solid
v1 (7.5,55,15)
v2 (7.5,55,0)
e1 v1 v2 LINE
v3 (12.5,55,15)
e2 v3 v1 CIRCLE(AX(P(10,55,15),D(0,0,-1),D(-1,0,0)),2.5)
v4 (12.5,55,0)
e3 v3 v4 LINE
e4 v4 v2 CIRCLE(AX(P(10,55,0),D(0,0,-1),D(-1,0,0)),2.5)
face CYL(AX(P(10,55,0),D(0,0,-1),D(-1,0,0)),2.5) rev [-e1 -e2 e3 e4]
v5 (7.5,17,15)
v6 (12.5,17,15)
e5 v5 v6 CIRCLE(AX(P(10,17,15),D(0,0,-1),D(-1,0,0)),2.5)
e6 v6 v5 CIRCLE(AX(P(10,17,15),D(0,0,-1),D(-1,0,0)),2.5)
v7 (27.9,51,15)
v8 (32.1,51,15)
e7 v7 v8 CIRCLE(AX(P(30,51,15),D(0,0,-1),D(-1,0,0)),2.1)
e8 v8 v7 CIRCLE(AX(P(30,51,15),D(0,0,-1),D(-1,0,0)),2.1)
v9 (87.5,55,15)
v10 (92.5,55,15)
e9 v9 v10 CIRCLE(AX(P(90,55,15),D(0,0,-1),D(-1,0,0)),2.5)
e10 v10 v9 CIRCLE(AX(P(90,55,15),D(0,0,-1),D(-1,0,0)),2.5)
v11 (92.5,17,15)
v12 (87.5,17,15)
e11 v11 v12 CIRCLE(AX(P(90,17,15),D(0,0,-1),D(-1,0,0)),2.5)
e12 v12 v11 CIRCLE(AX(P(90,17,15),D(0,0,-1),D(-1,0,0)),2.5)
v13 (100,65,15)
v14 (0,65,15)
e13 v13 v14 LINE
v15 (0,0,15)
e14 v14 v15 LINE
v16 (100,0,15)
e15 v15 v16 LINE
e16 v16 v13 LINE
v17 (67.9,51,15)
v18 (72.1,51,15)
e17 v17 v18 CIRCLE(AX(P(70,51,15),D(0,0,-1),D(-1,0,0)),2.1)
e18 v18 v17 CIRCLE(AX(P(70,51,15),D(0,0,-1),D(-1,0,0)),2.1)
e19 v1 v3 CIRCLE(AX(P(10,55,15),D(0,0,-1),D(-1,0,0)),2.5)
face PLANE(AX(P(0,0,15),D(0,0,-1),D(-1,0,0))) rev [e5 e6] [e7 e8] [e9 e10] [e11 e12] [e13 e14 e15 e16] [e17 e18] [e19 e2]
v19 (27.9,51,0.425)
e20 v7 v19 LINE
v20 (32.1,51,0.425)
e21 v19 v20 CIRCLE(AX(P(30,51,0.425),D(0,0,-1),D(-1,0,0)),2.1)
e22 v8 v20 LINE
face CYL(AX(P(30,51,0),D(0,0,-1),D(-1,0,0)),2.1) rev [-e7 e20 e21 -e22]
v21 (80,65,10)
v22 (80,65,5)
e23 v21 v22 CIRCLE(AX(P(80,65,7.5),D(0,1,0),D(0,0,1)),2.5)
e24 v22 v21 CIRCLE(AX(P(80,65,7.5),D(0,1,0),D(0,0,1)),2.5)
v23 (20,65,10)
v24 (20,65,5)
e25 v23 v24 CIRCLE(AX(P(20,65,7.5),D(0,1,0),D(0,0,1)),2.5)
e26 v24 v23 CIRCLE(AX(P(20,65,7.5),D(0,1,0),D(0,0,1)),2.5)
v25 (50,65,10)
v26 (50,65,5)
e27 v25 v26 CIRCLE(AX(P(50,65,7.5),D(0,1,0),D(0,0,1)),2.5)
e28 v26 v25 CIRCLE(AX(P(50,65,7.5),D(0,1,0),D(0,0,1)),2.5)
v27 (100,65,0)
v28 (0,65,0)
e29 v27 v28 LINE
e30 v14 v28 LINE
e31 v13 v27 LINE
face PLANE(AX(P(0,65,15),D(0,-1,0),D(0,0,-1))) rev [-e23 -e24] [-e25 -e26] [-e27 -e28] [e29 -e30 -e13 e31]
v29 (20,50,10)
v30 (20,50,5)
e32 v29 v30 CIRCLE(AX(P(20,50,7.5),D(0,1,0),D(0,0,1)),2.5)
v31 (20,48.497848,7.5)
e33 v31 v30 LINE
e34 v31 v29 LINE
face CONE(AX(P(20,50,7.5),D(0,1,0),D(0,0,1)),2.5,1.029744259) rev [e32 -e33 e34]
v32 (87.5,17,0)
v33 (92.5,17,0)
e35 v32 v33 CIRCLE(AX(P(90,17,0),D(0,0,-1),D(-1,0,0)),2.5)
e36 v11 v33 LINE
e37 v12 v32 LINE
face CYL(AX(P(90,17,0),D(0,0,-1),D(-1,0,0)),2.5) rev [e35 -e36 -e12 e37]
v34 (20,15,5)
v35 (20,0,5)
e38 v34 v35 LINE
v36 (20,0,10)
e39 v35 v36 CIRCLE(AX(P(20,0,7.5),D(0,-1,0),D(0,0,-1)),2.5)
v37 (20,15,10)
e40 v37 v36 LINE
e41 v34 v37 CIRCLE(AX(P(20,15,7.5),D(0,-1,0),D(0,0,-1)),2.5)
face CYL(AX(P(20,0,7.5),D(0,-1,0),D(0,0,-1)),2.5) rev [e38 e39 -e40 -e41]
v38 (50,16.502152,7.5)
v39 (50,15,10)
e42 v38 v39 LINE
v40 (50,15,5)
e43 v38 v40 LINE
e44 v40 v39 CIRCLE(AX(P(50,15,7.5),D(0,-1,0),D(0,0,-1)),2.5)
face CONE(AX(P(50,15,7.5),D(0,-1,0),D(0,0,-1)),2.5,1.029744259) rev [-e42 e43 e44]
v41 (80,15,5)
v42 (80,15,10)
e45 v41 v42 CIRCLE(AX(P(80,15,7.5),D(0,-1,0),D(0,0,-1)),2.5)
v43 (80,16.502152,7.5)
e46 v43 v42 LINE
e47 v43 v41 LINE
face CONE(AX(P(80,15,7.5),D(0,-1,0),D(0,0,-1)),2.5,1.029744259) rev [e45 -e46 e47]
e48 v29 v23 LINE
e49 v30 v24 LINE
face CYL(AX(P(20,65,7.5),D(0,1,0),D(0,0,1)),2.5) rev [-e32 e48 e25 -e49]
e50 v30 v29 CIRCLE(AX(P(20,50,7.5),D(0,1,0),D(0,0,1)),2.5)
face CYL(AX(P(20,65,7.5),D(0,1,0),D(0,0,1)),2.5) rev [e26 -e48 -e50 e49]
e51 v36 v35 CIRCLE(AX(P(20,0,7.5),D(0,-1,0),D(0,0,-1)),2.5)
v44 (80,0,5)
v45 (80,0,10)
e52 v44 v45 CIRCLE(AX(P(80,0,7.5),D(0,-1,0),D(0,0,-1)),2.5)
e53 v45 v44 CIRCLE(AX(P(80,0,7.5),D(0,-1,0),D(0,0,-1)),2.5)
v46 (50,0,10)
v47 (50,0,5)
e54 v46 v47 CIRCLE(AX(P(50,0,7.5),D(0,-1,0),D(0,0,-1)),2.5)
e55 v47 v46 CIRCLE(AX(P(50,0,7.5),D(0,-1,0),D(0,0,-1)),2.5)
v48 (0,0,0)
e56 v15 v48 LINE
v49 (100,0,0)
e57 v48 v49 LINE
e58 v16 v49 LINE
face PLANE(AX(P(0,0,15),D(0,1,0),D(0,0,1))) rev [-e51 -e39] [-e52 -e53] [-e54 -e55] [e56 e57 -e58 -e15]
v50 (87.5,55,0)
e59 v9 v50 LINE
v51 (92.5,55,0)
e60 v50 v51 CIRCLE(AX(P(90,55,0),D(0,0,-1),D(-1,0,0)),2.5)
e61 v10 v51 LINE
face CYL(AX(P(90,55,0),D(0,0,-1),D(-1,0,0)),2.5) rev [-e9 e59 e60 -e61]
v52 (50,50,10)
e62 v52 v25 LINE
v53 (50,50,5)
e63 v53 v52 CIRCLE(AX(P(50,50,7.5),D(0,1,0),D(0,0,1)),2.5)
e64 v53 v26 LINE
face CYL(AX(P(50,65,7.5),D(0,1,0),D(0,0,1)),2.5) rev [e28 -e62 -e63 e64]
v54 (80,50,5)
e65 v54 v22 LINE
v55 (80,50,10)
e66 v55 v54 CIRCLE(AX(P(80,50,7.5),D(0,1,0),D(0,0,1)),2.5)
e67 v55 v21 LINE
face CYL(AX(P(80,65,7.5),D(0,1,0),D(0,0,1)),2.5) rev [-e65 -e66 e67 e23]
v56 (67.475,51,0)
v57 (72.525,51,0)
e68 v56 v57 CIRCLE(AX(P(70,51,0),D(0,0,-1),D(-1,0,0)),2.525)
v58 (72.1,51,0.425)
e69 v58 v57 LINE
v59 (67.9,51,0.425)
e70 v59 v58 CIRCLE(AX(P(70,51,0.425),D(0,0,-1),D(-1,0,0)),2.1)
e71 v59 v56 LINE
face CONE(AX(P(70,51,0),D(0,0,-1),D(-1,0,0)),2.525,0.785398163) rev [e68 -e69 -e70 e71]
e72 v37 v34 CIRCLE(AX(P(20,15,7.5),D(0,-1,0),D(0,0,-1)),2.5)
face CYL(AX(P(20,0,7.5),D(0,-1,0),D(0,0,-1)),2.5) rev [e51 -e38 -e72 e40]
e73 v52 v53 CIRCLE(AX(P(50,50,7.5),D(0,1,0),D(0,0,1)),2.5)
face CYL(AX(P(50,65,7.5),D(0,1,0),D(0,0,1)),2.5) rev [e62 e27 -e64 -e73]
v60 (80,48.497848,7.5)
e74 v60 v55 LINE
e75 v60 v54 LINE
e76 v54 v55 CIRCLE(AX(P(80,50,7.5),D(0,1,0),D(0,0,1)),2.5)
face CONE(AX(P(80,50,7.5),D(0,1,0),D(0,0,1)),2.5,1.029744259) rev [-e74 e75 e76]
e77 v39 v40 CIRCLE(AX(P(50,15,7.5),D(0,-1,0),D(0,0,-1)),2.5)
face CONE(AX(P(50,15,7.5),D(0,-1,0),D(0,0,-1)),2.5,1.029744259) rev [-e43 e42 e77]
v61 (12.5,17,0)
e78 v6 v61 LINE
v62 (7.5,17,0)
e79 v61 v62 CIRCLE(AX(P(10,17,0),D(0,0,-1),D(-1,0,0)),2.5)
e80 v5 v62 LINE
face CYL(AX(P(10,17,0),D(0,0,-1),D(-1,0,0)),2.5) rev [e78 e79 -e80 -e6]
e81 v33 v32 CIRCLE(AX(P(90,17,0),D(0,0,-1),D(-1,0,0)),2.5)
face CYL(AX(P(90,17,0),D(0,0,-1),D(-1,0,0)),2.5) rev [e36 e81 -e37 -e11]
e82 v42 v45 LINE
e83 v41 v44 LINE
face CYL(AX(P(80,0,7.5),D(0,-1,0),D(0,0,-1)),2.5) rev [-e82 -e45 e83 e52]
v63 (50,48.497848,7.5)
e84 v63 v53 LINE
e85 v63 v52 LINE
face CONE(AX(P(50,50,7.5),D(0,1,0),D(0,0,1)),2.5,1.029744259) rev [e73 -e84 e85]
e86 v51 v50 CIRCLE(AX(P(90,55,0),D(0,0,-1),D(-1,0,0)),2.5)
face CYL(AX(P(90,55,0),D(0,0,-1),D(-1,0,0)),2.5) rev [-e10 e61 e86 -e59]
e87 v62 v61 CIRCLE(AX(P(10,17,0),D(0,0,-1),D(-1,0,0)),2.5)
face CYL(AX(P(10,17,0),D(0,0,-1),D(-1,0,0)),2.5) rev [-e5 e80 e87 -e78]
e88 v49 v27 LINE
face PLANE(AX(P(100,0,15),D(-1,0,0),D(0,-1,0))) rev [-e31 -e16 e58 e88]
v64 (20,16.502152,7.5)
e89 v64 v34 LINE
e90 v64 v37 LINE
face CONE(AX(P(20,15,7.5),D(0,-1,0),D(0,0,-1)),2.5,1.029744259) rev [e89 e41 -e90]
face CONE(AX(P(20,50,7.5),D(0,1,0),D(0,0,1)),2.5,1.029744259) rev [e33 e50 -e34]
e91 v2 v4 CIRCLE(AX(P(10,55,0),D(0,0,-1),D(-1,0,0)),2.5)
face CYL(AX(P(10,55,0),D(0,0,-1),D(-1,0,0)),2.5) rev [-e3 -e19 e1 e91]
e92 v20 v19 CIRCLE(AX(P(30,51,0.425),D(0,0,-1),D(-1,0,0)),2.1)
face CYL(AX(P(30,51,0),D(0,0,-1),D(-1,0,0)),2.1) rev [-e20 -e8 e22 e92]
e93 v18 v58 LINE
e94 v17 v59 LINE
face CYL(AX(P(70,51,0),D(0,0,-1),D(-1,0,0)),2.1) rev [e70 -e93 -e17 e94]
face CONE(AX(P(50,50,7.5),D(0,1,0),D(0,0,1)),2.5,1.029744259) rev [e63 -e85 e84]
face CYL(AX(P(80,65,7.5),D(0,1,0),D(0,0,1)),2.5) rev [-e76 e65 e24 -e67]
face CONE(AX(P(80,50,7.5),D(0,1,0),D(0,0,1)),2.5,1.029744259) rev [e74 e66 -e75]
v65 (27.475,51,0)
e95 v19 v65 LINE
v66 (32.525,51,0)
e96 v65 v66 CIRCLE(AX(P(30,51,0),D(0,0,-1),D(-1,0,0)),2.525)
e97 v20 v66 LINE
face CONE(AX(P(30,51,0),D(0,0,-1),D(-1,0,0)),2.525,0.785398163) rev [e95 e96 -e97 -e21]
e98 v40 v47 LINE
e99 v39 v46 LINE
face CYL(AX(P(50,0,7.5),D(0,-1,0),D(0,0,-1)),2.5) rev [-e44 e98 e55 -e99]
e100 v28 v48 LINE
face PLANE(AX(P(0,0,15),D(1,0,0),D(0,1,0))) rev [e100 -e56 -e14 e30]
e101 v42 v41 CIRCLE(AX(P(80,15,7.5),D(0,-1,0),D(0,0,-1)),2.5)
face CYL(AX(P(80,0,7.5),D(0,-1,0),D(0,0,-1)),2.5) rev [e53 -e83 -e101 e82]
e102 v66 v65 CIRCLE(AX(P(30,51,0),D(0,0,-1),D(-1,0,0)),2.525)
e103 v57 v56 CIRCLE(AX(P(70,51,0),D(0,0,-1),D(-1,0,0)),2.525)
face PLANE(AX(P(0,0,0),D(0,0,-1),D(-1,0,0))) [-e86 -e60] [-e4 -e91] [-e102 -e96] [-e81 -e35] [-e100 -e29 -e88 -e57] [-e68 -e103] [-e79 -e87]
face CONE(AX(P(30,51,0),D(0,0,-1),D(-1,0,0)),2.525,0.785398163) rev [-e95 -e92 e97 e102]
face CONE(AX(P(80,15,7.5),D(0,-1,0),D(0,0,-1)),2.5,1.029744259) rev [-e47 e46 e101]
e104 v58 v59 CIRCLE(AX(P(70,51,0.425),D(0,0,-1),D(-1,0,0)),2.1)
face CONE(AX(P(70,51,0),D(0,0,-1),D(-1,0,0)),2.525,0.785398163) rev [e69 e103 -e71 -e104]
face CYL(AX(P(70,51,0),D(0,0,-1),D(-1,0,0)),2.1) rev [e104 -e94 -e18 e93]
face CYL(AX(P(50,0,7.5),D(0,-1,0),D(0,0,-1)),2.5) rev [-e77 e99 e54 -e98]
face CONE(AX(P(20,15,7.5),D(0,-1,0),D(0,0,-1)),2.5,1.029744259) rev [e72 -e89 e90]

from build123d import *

# Parameters (mm, degrees)
SKETCH_1_W                   = 100
SKETCH_1_H                   = 65
EXTRUDE_1_DEPTH              = 15
HOLE_WIZARD_M6_1_D           = 5
HOLE_WIZARD_M6_1_DEPTH       = 15
HOLE_WIZARD_M6_1_TIP         = 1.502151548
HOLE_WIZARD_M6_2_D           = 5
HOLE_WIZARD_M6_2_DEPTH       = 15
HOLE_WIZARD_M6_2_TIP         = 1.502151548
HOLE_WIZARD_M5_1_D           = 4.2
HOLE_WIZARD_M5_1_CSINK_D     = 5.05
HOLE_WIZARD_M5_1_CSINK_ANGLE = 90
HOLE_WIZARD_M6_3_D           = 5


with BuildPart() as part:
    # 草图1 → 凸台-拉伸1 (new body)
    with BuildSketch(Plane.XY):
        with Locations((50, 32.5)):
            Rectangle(SKETCH_1_W, SKETCH_1_H)
    extrude(amount=EXTRUDE_1_DEPTH)

    # M6 螺纹孔1
    with Locations(Plane(origin=(0, 65, 0), x_dir=(1, 0, 0), z_dir=(0, 1, 0))):
        with Locations((20, -7.5), (80, -7.5), (50, -7.5)):
            Hole(HOLE_WIZARD_M6_1_D / 2, depth=HOLE_WIZARD_M6_1_DEPTH)
            with Locations((0, 0, -(HOLE_WIZARD_M6_1_DEPTH + HOLE_WIZARD_M6_1_TIP / 2))):  # 118° drill point
                Cone(0, HOLE_WIZARD_M6_1_D / 2, HOLE_WIZARD_M6_1_TIP, mode=Mode.SUBTRACT)

    # M6 螺纹孔2
    with Locations(Plane(origin=(0, 0, 0), x_dir=(-1, 0, 0), z_dir=(0, -1, 0))):
        with Locations((-80, -7.5), (-50, -7.5), (-20, -7.5)):
            Hole(HOLE_WIZARD_M6_2_D / 2, depth=HOLE_WIZARD_M6_2_DEPTH)
            with Locations((0, 0, -(HOLE_WIZARD_M6_2_DEPTH + HOLE_WIZARD_M6_2_TIP / 2))):  # 118° drill point
                Cone(0, HOLE_WIZARD_M6_2_D / 2, HOLE_WIZARD_M6_2_TIP, mode=Mode.SUBTRACT)

    # M5 螺纹孔1 (through all)
    with Locations(Plane(origin=(0, 0, 0), x_dir=(-1, 0, 0), z_dir=(0, 0, -1))):
        with Locations((-70, 51), (-30, 51)):
            CounterSinkHole(HOLE_WIZARD_M5_1_D / 2, HOLE_WIZARD_M5_1_CSINK_D / 2, counter_sink_angle=HOLE_WIZARD_M5_1_CSINK_ANGLE)

    # M6 螺纹孔3 (through all)
    with Locations(Plane(origin=(0, 0, 0), x_dir=(-1, 0, 0), z_dir=(0, 0, -1))):
        with Locations((-90, 55), (-10, 55), (-90, 17), (-10, 17)):
            Hole(HOLE_WIZARD_M6_3_D / 2)


solid = part.part
